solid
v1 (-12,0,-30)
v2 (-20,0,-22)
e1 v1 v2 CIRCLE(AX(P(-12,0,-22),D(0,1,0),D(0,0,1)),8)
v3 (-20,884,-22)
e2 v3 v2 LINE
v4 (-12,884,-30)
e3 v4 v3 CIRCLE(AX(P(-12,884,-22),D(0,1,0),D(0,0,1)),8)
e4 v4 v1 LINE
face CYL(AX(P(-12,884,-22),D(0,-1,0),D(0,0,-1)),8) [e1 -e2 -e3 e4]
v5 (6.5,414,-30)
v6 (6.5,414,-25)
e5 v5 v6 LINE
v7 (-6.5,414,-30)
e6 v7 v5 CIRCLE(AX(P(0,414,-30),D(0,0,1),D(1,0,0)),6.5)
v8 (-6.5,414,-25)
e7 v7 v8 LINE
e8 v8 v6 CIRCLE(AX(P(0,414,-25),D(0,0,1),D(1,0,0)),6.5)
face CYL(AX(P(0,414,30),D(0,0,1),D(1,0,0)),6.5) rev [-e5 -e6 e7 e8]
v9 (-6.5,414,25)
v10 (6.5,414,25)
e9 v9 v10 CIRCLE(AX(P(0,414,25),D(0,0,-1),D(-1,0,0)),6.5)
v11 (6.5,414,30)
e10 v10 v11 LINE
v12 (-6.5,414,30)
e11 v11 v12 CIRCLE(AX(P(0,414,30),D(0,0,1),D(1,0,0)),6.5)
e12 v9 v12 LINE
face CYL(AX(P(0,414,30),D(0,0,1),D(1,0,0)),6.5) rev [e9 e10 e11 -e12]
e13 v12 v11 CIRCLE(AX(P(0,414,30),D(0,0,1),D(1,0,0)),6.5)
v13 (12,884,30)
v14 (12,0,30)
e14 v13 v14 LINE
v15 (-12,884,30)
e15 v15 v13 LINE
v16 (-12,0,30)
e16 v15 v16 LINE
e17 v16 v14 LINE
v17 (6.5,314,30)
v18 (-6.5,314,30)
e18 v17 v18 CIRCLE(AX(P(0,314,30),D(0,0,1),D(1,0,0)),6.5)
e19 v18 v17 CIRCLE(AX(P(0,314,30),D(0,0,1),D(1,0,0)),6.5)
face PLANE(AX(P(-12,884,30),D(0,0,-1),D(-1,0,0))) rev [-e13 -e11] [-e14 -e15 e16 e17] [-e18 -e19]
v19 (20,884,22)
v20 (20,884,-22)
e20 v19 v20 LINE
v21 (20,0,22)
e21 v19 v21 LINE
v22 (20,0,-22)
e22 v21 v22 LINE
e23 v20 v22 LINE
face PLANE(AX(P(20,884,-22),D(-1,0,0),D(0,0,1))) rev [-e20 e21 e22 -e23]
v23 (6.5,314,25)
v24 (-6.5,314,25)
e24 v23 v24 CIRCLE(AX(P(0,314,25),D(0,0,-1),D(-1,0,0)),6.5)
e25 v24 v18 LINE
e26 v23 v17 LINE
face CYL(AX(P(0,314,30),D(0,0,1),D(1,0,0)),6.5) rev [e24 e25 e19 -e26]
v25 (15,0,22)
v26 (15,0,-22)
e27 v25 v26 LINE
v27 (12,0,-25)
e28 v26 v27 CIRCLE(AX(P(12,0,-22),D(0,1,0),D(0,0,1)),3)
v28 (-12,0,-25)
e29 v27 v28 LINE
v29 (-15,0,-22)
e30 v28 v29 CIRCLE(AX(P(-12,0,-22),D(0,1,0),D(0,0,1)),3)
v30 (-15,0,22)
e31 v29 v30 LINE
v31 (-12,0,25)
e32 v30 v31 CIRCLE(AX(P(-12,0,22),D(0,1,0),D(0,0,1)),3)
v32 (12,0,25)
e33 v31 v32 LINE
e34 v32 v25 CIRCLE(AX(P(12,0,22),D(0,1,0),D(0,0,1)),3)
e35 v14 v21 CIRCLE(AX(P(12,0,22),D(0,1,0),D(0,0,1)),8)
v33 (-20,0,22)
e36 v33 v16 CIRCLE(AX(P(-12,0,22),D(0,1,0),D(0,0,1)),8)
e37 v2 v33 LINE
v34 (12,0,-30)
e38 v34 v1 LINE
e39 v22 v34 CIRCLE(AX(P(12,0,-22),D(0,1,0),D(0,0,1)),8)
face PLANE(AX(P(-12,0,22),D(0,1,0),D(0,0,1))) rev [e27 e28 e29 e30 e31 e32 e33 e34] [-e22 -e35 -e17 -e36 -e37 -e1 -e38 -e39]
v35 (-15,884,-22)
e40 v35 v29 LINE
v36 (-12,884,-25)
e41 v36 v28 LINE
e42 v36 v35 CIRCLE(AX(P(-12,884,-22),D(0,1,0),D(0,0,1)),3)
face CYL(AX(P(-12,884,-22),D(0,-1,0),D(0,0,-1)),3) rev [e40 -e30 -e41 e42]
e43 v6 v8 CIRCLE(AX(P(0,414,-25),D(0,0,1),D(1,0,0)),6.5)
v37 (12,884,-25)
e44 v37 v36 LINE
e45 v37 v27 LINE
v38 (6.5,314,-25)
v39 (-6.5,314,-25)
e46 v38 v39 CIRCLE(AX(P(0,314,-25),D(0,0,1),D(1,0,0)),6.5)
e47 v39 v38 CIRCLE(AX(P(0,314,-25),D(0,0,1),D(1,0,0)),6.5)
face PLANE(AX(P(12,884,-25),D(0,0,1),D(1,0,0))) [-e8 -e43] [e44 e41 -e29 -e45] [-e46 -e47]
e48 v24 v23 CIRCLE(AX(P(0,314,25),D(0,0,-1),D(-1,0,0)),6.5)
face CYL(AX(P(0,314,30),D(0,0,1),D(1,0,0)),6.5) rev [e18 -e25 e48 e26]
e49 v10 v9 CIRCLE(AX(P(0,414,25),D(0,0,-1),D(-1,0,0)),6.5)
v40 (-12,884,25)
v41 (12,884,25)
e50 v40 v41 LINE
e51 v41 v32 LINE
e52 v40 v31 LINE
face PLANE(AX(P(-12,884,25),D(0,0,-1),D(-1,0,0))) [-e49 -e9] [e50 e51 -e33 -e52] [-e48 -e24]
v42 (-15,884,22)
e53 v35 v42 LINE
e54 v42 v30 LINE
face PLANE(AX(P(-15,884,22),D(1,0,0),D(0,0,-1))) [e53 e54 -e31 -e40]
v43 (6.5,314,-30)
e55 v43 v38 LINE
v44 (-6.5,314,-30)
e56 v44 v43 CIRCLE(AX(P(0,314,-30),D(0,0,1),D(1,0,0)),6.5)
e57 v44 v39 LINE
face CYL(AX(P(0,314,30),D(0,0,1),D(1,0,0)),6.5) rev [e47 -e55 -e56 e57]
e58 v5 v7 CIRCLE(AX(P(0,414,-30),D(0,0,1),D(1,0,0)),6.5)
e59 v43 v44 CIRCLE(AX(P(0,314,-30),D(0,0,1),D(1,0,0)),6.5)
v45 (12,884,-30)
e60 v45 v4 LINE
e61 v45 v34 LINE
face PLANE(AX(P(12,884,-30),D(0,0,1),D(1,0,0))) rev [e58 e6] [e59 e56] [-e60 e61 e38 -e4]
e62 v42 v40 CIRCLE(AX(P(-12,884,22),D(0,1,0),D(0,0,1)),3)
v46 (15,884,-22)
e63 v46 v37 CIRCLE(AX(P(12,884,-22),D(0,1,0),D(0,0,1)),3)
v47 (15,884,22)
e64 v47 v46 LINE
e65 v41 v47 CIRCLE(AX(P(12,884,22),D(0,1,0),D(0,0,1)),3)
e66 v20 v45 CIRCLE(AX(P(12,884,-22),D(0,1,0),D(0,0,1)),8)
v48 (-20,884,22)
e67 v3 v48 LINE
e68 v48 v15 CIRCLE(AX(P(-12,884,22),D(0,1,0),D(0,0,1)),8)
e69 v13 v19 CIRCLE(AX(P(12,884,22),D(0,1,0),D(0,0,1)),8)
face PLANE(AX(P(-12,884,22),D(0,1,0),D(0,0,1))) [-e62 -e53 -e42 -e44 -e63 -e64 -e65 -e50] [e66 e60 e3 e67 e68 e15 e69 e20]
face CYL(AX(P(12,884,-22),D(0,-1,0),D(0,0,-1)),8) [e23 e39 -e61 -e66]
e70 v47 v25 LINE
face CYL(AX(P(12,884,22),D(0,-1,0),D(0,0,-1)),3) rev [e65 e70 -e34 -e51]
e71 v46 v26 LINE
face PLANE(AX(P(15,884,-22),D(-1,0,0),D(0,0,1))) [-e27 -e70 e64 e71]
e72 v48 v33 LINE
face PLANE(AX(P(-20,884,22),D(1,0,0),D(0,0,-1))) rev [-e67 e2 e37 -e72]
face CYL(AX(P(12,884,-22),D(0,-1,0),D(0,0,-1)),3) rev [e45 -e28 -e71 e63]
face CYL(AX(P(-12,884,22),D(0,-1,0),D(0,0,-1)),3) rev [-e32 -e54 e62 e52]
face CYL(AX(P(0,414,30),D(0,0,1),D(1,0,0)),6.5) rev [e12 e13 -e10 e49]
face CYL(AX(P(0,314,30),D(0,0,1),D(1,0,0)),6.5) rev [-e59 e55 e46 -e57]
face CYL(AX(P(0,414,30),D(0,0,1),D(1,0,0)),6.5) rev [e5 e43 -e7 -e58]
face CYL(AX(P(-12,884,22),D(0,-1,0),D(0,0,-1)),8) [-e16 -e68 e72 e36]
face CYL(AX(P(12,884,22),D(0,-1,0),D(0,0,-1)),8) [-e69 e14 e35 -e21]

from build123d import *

# Parameters (mm, degrees)
GB_T_6728_2002_RECTANGULAR_HOLLOW_SECTIO_DEPTH = 884
F_13_0_13_DIAMETER_HOLE1_D                     = 13


with BuildPart() as part:
    # Sketch14 → GB/T 6728-2002 rectangular hollow section 60X40X5(1) (new body)
    with BuildSketch(Plane(origin=(0, 0, 0), x_dir=(-1, 0, 0), z_dir=(0, 1, 0))):
        with BuildLine():
            Line((-12, -30), (12, -30))
            ThreePointArc((12, -30), (17.656854249, -27.656854249), (20, -22))
            Line((20, -22), (20, 22))
            ThreePointArc((20, 22), (17.656854249, 27.656854249), (12, 30))
            Line((12, 30), (-12, 30))
            ThreePointArc((-12, 30), (-17.656854249, 27.656854249), (-20, 22))
            Line((-20, 22), (-20, -22))
            ThreePointArc((-20, -22), (-17.656854249, -27.656854249), (-12, -30))
        make_face()
        with BuildLine():
            Line((-12, -25), (12, -25))
            ThreePointArc((12, -25), (14.121320344, -24.121320344), (15, -22))
            Line((15, -22), (15, 22))
            ThreePointArc((15, 22), (14.121320344, 24.121320344), (12, 25))
            Line((12, 25), (-12, 25))
            ThreePointArc((-12, 25), (-14.121320344, 24.121320344), (-15, 22))
            Line((-15, 22), (-15, -22))
            ThreePointArc((-15, -22), (-14.121320344, -24.121320344), (-12, -25))
        make_face(mode=Mode.SUBTRACT)
    extrude(amount=GB_T_6728_2002_RECTANGULAR_HOLLOW_SECTIO_DEPTH)

    # Ø13.0 (13) Diameter Hole1 (through all)
    with Locations(Plane.XY.offset(30)):
        with Locations((0, 414), (0, 314)):
            Hole(F_13_0_13_DIAMETER_HOLE1_D / 2)


solid = part.part
